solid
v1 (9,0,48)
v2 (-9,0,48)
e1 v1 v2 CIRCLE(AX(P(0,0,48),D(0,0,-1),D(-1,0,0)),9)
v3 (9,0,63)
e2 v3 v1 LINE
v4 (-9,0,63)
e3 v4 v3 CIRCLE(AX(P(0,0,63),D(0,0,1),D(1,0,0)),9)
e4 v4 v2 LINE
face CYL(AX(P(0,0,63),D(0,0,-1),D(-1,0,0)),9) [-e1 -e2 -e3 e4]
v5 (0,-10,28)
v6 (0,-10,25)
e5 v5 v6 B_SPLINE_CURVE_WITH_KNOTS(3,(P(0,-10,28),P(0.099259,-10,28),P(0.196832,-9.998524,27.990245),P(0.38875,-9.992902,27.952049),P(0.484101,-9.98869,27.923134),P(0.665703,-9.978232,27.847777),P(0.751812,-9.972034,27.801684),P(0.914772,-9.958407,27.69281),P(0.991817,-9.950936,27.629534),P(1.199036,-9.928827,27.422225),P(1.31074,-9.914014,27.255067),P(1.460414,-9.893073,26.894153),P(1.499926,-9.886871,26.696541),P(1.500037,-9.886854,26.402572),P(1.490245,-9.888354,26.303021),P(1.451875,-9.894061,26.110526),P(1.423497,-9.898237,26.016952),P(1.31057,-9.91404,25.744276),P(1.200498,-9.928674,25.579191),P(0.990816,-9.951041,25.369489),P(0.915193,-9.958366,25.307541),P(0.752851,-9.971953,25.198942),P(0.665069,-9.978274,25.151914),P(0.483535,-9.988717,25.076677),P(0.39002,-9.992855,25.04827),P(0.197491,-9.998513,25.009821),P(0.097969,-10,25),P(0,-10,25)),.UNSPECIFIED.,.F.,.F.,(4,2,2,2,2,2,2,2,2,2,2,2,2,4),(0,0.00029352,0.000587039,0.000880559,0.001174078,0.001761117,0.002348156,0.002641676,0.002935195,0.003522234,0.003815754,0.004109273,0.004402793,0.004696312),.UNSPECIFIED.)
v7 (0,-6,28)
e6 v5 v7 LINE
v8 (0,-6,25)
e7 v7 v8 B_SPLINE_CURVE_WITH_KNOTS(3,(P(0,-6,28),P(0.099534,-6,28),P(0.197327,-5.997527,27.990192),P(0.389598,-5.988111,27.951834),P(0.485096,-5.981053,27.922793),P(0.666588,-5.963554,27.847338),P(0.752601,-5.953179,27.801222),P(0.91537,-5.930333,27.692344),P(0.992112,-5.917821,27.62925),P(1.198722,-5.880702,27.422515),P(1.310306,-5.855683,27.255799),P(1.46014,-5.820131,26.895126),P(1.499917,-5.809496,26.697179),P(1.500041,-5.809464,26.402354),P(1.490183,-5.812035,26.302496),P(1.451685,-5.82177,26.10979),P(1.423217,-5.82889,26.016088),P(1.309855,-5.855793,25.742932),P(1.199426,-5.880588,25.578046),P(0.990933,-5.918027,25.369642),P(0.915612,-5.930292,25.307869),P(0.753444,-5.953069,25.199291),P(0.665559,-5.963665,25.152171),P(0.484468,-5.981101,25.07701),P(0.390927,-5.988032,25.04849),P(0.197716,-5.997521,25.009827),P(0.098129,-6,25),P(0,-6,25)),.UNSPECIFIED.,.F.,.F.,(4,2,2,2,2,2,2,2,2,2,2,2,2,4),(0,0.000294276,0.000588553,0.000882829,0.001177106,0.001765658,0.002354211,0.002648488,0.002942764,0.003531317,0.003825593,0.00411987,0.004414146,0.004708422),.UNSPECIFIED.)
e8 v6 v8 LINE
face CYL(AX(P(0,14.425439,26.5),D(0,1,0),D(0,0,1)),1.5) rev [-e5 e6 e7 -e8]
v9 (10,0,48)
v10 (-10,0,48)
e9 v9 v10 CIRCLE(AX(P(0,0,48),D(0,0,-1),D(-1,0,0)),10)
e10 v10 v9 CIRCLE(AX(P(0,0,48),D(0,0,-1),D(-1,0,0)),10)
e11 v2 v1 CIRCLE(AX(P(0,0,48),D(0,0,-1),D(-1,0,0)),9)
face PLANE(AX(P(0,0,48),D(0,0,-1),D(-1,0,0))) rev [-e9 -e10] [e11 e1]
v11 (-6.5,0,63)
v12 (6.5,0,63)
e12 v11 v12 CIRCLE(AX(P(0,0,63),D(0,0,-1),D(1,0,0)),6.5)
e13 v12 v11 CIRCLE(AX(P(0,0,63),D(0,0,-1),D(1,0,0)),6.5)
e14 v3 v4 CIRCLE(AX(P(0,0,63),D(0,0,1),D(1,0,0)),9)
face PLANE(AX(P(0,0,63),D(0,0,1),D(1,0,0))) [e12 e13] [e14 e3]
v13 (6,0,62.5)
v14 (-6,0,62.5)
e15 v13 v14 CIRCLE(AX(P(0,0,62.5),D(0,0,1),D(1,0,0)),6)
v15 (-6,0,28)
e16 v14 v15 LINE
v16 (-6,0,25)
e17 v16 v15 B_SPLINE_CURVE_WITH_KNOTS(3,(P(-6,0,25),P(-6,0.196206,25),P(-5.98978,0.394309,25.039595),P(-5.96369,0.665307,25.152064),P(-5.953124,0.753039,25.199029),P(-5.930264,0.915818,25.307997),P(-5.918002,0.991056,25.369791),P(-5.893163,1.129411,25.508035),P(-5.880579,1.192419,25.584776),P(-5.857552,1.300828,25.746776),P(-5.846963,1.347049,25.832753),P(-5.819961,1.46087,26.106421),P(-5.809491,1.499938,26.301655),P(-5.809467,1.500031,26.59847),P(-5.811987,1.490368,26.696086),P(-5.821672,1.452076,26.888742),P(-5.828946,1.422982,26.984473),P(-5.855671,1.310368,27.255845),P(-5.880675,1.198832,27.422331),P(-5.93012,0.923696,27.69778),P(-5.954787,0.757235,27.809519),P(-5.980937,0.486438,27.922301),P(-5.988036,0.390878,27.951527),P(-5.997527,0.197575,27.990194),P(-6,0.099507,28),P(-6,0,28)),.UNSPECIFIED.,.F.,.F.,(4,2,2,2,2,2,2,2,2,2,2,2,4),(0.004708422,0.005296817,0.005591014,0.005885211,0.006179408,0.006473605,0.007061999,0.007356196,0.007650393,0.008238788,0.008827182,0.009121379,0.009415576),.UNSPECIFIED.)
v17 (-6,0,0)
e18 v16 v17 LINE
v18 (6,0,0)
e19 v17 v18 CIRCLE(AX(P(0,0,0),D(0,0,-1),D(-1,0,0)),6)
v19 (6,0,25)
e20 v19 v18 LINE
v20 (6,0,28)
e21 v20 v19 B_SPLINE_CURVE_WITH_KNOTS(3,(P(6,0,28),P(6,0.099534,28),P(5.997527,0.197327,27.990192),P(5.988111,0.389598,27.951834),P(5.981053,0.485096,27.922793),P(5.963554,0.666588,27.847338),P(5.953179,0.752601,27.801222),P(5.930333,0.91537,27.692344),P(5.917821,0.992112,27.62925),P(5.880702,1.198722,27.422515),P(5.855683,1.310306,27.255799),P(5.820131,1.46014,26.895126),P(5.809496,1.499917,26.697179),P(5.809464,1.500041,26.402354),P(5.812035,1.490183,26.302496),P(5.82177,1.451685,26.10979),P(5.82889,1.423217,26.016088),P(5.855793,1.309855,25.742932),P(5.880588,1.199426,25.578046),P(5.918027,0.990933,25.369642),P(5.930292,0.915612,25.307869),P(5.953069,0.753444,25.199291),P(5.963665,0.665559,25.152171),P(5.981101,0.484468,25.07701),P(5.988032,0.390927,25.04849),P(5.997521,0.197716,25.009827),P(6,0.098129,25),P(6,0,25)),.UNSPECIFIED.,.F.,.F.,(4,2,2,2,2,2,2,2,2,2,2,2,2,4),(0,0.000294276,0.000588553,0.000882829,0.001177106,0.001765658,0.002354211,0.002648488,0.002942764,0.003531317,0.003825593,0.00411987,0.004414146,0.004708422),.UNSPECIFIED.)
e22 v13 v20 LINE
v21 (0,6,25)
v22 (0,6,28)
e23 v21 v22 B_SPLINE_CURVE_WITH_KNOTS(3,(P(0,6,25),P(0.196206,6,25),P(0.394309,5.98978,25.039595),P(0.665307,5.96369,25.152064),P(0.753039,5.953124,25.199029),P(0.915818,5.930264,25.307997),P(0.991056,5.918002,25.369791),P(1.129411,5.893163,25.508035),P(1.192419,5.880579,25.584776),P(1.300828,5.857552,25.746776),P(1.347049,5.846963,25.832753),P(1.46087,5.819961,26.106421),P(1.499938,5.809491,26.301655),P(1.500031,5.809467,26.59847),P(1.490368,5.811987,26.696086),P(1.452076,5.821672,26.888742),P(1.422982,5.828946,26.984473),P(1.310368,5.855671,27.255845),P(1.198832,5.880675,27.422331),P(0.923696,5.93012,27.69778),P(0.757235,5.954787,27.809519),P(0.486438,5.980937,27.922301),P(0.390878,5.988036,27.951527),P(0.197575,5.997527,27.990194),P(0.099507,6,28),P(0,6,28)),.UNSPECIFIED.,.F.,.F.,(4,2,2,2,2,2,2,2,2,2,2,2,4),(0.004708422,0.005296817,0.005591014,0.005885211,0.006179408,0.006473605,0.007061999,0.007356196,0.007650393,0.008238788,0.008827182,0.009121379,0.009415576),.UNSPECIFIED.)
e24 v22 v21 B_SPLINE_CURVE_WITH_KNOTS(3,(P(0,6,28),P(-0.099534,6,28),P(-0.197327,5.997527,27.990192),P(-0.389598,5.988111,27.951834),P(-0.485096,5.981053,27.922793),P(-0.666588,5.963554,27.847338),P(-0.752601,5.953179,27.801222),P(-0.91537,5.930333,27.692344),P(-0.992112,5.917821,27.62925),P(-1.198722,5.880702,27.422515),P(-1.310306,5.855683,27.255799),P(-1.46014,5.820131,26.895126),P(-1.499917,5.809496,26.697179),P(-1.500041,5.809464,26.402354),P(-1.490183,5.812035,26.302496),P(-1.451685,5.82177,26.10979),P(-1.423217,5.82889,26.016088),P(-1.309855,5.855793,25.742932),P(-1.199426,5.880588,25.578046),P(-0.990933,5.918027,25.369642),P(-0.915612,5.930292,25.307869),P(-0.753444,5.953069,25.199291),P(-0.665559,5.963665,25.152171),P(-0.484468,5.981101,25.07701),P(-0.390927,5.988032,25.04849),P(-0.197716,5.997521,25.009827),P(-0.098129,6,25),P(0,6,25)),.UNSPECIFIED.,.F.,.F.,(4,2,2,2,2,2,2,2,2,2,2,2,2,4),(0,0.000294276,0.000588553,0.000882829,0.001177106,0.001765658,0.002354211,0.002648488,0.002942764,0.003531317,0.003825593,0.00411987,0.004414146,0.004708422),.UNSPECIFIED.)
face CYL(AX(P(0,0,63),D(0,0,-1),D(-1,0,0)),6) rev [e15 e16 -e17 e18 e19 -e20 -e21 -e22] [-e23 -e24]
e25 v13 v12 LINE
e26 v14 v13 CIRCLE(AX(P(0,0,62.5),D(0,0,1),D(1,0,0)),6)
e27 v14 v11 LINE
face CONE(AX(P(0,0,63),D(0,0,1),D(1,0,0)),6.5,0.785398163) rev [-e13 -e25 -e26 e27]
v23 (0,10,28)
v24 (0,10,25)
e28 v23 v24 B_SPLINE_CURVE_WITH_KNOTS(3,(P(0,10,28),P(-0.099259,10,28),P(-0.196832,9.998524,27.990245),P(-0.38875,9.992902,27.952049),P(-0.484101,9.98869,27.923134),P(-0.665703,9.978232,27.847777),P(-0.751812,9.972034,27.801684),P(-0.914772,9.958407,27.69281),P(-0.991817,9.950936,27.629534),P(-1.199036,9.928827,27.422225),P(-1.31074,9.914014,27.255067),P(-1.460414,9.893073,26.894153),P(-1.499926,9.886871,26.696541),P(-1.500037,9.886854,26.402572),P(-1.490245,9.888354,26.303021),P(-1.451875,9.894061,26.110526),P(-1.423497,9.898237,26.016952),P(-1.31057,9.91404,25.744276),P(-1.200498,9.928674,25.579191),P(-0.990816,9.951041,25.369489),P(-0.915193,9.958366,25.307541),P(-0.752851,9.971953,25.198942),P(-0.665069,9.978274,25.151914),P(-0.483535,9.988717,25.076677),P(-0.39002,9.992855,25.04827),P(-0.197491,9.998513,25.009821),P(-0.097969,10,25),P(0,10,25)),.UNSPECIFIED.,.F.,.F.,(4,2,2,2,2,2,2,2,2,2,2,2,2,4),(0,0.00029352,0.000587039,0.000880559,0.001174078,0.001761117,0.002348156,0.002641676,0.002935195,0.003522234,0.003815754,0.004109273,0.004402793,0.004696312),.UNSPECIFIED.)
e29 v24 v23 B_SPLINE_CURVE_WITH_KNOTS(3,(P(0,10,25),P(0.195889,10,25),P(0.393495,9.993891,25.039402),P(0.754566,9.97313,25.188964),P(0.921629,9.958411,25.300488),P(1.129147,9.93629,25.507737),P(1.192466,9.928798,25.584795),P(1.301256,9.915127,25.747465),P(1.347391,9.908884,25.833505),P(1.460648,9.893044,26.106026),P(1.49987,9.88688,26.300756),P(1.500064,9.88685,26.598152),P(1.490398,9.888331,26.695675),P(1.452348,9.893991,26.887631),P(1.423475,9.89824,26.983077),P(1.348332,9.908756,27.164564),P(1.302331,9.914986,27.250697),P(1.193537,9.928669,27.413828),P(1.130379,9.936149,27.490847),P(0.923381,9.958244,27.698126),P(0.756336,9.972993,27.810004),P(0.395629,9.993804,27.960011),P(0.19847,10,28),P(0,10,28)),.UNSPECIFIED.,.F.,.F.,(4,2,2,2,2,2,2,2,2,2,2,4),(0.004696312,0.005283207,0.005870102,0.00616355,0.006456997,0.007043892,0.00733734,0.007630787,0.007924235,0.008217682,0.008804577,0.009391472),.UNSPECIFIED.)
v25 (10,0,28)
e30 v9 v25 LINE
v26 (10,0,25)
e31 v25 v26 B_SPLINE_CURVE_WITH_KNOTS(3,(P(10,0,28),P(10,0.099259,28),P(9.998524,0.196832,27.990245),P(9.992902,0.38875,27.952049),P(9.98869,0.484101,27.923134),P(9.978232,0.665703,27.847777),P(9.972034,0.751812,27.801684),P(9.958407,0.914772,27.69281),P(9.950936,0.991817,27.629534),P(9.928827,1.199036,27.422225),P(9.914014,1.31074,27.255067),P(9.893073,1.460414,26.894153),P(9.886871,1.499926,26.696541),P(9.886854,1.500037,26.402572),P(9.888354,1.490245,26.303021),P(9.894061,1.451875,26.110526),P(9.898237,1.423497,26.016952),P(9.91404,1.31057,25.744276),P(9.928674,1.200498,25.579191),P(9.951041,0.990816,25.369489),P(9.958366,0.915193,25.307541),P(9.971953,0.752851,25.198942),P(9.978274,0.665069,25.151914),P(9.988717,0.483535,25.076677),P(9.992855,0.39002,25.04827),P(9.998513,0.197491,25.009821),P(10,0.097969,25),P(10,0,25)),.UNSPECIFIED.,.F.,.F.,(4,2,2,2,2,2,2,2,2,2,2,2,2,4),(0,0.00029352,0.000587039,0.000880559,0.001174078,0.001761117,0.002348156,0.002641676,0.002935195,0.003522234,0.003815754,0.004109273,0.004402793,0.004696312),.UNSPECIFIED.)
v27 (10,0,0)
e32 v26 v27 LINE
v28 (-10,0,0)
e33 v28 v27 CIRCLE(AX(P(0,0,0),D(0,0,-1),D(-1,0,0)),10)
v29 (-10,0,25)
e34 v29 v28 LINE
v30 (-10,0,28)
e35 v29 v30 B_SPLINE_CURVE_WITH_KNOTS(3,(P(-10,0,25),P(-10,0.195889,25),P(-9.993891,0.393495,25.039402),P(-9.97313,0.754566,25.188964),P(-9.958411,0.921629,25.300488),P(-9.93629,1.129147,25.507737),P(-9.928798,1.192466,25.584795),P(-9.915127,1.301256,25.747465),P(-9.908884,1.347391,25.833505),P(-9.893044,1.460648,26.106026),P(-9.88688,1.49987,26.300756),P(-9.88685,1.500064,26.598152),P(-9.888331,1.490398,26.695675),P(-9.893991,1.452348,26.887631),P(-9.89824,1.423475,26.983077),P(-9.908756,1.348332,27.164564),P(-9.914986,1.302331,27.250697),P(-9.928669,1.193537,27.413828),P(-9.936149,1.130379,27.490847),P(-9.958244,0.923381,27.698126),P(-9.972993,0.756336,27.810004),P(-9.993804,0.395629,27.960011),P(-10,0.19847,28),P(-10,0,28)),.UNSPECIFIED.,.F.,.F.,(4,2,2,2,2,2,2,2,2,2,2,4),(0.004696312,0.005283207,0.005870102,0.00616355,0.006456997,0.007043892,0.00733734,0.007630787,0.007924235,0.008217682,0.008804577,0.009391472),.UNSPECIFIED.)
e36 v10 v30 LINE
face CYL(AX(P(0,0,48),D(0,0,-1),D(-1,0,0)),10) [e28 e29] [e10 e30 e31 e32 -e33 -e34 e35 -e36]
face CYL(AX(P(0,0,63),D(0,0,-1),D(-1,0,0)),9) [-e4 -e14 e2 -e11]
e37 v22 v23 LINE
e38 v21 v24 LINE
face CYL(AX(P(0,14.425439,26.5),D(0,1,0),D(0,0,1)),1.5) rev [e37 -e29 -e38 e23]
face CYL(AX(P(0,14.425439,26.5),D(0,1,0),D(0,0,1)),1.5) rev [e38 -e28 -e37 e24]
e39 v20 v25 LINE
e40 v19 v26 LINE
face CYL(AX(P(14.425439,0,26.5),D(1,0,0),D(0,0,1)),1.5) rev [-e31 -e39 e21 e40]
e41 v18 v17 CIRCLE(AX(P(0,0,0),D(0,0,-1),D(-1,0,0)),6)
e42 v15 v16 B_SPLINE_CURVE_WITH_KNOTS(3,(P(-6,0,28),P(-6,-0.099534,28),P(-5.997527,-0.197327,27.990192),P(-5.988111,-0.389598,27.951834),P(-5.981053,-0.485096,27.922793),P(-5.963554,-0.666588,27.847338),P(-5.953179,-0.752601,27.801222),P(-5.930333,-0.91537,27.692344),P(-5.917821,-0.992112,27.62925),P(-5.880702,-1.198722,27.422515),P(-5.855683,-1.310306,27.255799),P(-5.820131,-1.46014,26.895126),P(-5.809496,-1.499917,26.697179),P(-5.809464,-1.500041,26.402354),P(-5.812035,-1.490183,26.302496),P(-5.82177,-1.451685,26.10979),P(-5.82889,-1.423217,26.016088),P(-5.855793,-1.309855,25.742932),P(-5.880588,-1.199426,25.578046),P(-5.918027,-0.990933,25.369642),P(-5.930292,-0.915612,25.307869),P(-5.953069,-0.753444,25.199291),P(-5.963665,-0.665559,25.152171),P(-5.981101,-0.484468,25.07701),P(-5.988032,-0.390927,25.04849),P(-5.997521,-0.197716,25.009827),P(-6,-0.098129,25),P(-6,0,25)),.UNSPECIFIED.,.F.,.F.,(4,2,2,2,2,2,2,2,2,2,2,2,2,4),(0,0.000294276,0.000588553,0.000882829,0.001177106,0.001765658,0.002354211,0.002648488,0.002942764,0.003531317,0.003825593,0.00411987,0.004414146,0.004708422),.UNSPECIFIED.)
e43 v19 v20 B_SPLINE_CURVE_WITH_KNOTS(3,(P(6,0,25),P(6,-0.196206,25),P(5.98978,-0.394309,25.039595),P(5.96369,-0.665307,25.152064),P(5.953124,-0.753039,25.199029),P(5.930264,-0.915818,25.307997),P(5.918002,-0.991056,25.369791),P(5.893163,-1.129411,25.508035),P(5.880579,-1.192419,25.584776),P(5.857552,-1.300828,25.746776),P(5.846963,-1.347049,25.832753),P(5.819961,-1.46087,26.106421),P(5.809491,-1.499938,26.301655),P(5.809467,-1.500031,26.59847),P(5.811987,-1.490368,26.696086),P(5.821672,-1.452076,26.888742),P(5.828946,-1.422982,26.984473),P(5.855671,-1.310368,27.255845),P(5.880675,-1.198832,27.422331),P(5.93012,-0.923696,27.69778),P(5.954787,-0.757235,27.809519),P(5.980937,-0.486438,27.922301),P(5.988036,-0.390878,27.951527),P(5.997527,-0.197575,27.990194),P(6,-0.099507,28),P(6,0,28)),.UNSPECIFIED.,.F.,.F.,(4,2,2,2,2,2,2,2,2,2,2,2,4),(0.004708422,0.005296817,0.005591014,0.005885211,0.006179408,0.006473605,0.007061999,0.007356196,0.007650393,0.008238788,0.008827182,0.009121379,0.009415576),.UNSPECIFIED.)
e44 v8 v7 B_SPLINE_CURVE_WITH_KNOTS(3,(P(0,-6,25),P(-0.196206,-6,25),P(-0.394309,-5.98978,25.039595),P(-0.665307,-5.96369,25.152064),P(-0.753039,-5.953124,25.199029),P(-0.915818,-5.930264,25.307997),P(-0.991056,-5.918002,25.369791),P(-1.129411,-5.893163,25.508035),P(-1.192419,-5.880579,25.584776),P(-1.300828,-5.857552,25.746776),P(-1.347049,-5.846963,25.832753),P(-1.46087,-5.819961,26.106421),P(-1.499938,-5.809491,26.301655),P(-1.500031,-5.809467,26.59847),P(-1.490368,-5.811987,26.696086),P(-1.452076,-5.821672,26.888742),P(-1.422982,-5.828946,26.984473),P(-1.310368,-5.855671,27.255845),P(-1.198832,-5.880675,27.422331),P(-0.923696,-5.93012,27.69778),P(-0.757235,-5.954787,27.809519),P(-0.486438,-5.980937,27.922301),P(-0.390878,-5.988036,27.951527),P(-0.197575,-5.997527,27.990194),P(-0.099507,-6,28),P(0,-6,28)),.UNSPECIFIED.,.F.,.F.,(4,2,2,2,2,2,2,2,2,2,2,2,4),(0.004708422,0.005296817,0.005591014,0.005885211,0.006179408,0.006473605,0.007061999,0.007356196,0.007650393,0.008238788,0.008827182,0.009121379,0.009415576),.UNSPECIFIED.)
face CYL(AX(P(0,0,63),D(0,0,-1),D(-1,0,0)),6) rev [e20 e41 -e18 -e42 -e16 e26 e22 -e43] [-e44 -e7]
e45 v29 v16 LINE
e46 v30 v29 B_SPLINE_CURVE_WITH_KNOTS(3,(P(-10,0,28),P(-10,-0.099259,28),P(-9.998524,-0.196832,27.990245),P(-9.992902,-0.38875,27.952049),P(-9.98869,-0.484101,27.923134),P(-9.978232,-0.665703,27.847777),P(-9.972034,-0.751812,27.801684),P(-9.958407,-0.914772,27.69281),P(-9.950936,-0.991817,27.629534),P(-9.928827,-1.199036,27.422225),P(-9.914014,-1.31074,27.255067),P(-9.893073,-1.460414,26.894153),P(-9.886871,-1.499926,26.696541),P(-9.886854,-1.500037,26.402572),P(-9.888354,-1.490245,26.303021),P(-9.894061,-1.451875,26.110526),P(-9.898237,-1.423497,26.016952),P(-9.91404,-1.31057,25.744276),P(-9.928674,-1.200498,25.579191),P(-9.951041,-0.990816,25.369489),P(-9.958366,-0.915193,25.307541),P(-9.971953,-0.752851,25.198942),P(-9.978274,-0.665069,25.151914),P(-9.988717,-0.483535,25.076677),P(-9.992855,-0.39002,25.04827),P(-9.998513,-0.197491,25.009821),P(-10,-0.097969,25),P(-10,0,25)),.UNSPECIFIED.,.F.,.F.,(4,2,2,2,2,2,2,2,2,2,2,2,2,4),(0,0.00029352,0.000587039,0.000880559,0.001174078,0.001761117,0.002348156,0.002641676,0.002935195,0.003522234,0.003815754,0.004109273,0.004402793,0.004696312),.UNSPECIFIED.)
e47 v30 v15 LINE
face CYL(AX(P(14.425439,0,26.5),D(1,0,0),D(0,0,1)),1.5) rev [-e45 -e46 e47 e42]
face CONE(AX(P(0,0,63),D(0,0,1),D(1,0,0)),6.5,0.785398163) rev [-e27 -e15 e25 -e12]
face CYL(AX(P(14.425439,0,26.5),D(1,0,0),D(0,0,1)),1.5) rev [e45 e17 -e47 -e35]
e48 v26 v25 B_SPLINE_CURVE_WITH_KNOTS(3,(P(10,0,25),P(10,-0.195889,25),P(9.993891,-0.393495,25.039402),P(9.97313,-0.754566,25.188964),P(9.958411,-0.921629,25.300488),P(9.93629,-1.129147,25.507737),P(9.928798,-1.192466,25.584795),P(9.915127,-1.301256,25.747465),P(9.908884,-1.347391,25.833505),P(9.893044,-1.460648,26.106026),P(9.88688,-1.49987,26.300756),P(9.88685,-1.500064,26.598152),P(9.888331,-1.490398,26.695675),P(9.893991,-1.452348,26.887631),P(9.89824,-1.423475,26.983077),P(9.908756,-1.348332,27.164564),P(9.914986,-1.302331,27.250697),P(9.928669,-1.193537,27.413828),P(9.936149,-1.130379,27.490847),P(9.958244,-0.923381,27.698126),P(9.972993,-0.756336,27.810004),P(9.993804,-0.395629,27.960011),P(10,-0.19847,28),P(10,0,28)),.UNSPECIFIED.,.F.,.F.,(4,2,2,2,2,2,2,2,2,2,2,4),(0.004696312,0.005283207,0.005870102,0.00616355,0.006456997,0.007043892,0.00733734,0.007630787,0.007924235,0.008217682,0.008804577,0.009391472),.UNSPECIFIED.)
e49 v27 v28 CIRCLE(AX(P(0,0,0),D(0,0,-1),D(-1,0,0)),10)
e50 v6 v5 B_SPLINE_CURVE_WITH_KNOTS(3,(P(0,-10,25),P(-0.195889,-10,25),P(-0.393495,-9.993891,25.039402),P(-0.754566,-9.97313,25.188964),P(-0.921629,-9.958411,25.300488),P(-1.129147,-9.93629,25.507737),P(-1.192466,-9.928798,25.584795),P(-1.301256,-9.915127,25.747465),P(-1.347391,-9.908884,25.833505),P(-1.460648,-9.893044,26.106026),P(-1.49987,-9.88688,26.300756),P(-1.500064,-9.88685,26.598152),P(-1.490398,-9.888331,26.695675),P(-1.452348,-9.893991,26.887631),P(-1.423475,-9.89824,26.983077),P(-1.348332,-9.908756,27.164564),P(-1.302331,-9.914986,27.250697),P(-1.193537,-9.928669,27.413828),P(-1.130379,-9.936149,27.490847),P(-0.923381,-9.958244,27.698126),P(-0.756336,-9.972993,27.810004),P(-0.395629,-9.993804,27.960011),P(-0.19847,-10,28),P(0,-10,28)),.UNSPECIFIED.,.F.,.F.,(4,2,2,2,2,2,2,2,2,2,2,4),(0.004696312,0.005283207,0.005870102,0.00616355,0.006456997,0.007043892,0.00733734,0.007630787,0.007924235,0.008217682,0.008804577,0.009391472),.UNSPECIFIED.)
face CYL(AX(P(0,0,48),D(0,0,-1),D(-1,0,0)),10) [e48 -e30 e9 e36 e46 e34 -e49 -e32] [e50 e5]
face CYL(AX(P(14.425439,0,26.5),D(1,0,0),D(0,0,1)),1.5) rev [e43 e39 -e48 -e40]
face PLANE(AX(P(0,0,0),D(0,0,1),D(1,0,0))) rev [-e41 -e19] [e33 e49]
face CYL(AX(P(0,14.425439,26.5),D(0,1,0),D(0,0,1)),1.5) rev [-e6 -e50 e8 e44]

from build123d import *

# Parameters (mm, degrees)
SKETCH1_R           = 9
BOSS_EXTRUDE1_DEPTH = 63
SKETCH2_R           = 10
BOSS_EXTRUDE2_DEPTH = 48
SKETCH3_R           = 6
CUT_EXTRUDE1_DEPTH  = 65.567793829
SKETCH4_W           = 1.5
SKETCH4_H           = 27.68
CIRPATTERN1_COUNT   = 4
CHAMFER1_SIZE       = 0.5


with BuildPart() as part:
    # Sketch1 → Boss-Extrude1 (new body)
    with BuildSketch(Plane.XY):
        Circle(SKETCH1_R)
    extrude(amount=BOSS_EXTRUDE1_DEPTH)

    # Sketch2 → Boss-Extrude2 (add)
    with BuildSketch(Plane(origin=(0, 0, 0), x_dir=(-1, 0, 0), z_dir=(0, 0, -1))):
        Circle(SKETCH2_R)
    extrude(amount=-BOSS_EXTRUDE2_DEPTH)

    # Sketch3 → Cut-Extrude1 (cut, through all)
    with BuildSketch(Plane(origin=(0, 0, 0), x_dir=(-1, 0, 0), z_dir=(0, 0, -1))):
        Circle(SKETCH3_R)
    extrude(amount=-CUT_EXTRUDE1_DEPTH, mode=Mode.SUBTRACT)

    # Sketch4 → Cut-Revolve1 (revolve, cut)
    with BuildSketch(Plane(origin=(0, 0, 0), x_dir=(0, 0, -1), z_dir=(1, 0, 0)), mode=Mode.PRIVATE) as cut_revolve1_sk:
        with Locations((-25.75, 0.585439351)):
            Rectangle(SKETCH4_W, SKETCH4_H)
    cut_revolve1 = revolve(cut_revolve1_sk.sketch.rotate(Axis((0, 14.425439351, 26.5), (0, -1, 0)), 180), axis=Axis((0, 14.425439351, 26.5), (0, -1, 0)), mode=Mode.SUBTRACT)

    # CirPattern1: Cut-Revolve1 ×4 about axis
    cirpattern1_axis = Axis((0, 0, 48), (0, 0, -1))
    for i in range(1, CIRPATTERN1_COUNT):
        add(cut_revolve1.rotate(cirpattern1_axis, i * 360 / CIRPATTERN1_COUNT), mode=Mode.SUBTRACT)

    # Chamfer1
    chamfer1_edges = [part.edges().sort_by_distance(p)[0] for p in [
        (6, 0, 63),
    ]]
    chamfer(chamfer1_edges, length=CHAMFER1_SIZE)


solid = part.part
